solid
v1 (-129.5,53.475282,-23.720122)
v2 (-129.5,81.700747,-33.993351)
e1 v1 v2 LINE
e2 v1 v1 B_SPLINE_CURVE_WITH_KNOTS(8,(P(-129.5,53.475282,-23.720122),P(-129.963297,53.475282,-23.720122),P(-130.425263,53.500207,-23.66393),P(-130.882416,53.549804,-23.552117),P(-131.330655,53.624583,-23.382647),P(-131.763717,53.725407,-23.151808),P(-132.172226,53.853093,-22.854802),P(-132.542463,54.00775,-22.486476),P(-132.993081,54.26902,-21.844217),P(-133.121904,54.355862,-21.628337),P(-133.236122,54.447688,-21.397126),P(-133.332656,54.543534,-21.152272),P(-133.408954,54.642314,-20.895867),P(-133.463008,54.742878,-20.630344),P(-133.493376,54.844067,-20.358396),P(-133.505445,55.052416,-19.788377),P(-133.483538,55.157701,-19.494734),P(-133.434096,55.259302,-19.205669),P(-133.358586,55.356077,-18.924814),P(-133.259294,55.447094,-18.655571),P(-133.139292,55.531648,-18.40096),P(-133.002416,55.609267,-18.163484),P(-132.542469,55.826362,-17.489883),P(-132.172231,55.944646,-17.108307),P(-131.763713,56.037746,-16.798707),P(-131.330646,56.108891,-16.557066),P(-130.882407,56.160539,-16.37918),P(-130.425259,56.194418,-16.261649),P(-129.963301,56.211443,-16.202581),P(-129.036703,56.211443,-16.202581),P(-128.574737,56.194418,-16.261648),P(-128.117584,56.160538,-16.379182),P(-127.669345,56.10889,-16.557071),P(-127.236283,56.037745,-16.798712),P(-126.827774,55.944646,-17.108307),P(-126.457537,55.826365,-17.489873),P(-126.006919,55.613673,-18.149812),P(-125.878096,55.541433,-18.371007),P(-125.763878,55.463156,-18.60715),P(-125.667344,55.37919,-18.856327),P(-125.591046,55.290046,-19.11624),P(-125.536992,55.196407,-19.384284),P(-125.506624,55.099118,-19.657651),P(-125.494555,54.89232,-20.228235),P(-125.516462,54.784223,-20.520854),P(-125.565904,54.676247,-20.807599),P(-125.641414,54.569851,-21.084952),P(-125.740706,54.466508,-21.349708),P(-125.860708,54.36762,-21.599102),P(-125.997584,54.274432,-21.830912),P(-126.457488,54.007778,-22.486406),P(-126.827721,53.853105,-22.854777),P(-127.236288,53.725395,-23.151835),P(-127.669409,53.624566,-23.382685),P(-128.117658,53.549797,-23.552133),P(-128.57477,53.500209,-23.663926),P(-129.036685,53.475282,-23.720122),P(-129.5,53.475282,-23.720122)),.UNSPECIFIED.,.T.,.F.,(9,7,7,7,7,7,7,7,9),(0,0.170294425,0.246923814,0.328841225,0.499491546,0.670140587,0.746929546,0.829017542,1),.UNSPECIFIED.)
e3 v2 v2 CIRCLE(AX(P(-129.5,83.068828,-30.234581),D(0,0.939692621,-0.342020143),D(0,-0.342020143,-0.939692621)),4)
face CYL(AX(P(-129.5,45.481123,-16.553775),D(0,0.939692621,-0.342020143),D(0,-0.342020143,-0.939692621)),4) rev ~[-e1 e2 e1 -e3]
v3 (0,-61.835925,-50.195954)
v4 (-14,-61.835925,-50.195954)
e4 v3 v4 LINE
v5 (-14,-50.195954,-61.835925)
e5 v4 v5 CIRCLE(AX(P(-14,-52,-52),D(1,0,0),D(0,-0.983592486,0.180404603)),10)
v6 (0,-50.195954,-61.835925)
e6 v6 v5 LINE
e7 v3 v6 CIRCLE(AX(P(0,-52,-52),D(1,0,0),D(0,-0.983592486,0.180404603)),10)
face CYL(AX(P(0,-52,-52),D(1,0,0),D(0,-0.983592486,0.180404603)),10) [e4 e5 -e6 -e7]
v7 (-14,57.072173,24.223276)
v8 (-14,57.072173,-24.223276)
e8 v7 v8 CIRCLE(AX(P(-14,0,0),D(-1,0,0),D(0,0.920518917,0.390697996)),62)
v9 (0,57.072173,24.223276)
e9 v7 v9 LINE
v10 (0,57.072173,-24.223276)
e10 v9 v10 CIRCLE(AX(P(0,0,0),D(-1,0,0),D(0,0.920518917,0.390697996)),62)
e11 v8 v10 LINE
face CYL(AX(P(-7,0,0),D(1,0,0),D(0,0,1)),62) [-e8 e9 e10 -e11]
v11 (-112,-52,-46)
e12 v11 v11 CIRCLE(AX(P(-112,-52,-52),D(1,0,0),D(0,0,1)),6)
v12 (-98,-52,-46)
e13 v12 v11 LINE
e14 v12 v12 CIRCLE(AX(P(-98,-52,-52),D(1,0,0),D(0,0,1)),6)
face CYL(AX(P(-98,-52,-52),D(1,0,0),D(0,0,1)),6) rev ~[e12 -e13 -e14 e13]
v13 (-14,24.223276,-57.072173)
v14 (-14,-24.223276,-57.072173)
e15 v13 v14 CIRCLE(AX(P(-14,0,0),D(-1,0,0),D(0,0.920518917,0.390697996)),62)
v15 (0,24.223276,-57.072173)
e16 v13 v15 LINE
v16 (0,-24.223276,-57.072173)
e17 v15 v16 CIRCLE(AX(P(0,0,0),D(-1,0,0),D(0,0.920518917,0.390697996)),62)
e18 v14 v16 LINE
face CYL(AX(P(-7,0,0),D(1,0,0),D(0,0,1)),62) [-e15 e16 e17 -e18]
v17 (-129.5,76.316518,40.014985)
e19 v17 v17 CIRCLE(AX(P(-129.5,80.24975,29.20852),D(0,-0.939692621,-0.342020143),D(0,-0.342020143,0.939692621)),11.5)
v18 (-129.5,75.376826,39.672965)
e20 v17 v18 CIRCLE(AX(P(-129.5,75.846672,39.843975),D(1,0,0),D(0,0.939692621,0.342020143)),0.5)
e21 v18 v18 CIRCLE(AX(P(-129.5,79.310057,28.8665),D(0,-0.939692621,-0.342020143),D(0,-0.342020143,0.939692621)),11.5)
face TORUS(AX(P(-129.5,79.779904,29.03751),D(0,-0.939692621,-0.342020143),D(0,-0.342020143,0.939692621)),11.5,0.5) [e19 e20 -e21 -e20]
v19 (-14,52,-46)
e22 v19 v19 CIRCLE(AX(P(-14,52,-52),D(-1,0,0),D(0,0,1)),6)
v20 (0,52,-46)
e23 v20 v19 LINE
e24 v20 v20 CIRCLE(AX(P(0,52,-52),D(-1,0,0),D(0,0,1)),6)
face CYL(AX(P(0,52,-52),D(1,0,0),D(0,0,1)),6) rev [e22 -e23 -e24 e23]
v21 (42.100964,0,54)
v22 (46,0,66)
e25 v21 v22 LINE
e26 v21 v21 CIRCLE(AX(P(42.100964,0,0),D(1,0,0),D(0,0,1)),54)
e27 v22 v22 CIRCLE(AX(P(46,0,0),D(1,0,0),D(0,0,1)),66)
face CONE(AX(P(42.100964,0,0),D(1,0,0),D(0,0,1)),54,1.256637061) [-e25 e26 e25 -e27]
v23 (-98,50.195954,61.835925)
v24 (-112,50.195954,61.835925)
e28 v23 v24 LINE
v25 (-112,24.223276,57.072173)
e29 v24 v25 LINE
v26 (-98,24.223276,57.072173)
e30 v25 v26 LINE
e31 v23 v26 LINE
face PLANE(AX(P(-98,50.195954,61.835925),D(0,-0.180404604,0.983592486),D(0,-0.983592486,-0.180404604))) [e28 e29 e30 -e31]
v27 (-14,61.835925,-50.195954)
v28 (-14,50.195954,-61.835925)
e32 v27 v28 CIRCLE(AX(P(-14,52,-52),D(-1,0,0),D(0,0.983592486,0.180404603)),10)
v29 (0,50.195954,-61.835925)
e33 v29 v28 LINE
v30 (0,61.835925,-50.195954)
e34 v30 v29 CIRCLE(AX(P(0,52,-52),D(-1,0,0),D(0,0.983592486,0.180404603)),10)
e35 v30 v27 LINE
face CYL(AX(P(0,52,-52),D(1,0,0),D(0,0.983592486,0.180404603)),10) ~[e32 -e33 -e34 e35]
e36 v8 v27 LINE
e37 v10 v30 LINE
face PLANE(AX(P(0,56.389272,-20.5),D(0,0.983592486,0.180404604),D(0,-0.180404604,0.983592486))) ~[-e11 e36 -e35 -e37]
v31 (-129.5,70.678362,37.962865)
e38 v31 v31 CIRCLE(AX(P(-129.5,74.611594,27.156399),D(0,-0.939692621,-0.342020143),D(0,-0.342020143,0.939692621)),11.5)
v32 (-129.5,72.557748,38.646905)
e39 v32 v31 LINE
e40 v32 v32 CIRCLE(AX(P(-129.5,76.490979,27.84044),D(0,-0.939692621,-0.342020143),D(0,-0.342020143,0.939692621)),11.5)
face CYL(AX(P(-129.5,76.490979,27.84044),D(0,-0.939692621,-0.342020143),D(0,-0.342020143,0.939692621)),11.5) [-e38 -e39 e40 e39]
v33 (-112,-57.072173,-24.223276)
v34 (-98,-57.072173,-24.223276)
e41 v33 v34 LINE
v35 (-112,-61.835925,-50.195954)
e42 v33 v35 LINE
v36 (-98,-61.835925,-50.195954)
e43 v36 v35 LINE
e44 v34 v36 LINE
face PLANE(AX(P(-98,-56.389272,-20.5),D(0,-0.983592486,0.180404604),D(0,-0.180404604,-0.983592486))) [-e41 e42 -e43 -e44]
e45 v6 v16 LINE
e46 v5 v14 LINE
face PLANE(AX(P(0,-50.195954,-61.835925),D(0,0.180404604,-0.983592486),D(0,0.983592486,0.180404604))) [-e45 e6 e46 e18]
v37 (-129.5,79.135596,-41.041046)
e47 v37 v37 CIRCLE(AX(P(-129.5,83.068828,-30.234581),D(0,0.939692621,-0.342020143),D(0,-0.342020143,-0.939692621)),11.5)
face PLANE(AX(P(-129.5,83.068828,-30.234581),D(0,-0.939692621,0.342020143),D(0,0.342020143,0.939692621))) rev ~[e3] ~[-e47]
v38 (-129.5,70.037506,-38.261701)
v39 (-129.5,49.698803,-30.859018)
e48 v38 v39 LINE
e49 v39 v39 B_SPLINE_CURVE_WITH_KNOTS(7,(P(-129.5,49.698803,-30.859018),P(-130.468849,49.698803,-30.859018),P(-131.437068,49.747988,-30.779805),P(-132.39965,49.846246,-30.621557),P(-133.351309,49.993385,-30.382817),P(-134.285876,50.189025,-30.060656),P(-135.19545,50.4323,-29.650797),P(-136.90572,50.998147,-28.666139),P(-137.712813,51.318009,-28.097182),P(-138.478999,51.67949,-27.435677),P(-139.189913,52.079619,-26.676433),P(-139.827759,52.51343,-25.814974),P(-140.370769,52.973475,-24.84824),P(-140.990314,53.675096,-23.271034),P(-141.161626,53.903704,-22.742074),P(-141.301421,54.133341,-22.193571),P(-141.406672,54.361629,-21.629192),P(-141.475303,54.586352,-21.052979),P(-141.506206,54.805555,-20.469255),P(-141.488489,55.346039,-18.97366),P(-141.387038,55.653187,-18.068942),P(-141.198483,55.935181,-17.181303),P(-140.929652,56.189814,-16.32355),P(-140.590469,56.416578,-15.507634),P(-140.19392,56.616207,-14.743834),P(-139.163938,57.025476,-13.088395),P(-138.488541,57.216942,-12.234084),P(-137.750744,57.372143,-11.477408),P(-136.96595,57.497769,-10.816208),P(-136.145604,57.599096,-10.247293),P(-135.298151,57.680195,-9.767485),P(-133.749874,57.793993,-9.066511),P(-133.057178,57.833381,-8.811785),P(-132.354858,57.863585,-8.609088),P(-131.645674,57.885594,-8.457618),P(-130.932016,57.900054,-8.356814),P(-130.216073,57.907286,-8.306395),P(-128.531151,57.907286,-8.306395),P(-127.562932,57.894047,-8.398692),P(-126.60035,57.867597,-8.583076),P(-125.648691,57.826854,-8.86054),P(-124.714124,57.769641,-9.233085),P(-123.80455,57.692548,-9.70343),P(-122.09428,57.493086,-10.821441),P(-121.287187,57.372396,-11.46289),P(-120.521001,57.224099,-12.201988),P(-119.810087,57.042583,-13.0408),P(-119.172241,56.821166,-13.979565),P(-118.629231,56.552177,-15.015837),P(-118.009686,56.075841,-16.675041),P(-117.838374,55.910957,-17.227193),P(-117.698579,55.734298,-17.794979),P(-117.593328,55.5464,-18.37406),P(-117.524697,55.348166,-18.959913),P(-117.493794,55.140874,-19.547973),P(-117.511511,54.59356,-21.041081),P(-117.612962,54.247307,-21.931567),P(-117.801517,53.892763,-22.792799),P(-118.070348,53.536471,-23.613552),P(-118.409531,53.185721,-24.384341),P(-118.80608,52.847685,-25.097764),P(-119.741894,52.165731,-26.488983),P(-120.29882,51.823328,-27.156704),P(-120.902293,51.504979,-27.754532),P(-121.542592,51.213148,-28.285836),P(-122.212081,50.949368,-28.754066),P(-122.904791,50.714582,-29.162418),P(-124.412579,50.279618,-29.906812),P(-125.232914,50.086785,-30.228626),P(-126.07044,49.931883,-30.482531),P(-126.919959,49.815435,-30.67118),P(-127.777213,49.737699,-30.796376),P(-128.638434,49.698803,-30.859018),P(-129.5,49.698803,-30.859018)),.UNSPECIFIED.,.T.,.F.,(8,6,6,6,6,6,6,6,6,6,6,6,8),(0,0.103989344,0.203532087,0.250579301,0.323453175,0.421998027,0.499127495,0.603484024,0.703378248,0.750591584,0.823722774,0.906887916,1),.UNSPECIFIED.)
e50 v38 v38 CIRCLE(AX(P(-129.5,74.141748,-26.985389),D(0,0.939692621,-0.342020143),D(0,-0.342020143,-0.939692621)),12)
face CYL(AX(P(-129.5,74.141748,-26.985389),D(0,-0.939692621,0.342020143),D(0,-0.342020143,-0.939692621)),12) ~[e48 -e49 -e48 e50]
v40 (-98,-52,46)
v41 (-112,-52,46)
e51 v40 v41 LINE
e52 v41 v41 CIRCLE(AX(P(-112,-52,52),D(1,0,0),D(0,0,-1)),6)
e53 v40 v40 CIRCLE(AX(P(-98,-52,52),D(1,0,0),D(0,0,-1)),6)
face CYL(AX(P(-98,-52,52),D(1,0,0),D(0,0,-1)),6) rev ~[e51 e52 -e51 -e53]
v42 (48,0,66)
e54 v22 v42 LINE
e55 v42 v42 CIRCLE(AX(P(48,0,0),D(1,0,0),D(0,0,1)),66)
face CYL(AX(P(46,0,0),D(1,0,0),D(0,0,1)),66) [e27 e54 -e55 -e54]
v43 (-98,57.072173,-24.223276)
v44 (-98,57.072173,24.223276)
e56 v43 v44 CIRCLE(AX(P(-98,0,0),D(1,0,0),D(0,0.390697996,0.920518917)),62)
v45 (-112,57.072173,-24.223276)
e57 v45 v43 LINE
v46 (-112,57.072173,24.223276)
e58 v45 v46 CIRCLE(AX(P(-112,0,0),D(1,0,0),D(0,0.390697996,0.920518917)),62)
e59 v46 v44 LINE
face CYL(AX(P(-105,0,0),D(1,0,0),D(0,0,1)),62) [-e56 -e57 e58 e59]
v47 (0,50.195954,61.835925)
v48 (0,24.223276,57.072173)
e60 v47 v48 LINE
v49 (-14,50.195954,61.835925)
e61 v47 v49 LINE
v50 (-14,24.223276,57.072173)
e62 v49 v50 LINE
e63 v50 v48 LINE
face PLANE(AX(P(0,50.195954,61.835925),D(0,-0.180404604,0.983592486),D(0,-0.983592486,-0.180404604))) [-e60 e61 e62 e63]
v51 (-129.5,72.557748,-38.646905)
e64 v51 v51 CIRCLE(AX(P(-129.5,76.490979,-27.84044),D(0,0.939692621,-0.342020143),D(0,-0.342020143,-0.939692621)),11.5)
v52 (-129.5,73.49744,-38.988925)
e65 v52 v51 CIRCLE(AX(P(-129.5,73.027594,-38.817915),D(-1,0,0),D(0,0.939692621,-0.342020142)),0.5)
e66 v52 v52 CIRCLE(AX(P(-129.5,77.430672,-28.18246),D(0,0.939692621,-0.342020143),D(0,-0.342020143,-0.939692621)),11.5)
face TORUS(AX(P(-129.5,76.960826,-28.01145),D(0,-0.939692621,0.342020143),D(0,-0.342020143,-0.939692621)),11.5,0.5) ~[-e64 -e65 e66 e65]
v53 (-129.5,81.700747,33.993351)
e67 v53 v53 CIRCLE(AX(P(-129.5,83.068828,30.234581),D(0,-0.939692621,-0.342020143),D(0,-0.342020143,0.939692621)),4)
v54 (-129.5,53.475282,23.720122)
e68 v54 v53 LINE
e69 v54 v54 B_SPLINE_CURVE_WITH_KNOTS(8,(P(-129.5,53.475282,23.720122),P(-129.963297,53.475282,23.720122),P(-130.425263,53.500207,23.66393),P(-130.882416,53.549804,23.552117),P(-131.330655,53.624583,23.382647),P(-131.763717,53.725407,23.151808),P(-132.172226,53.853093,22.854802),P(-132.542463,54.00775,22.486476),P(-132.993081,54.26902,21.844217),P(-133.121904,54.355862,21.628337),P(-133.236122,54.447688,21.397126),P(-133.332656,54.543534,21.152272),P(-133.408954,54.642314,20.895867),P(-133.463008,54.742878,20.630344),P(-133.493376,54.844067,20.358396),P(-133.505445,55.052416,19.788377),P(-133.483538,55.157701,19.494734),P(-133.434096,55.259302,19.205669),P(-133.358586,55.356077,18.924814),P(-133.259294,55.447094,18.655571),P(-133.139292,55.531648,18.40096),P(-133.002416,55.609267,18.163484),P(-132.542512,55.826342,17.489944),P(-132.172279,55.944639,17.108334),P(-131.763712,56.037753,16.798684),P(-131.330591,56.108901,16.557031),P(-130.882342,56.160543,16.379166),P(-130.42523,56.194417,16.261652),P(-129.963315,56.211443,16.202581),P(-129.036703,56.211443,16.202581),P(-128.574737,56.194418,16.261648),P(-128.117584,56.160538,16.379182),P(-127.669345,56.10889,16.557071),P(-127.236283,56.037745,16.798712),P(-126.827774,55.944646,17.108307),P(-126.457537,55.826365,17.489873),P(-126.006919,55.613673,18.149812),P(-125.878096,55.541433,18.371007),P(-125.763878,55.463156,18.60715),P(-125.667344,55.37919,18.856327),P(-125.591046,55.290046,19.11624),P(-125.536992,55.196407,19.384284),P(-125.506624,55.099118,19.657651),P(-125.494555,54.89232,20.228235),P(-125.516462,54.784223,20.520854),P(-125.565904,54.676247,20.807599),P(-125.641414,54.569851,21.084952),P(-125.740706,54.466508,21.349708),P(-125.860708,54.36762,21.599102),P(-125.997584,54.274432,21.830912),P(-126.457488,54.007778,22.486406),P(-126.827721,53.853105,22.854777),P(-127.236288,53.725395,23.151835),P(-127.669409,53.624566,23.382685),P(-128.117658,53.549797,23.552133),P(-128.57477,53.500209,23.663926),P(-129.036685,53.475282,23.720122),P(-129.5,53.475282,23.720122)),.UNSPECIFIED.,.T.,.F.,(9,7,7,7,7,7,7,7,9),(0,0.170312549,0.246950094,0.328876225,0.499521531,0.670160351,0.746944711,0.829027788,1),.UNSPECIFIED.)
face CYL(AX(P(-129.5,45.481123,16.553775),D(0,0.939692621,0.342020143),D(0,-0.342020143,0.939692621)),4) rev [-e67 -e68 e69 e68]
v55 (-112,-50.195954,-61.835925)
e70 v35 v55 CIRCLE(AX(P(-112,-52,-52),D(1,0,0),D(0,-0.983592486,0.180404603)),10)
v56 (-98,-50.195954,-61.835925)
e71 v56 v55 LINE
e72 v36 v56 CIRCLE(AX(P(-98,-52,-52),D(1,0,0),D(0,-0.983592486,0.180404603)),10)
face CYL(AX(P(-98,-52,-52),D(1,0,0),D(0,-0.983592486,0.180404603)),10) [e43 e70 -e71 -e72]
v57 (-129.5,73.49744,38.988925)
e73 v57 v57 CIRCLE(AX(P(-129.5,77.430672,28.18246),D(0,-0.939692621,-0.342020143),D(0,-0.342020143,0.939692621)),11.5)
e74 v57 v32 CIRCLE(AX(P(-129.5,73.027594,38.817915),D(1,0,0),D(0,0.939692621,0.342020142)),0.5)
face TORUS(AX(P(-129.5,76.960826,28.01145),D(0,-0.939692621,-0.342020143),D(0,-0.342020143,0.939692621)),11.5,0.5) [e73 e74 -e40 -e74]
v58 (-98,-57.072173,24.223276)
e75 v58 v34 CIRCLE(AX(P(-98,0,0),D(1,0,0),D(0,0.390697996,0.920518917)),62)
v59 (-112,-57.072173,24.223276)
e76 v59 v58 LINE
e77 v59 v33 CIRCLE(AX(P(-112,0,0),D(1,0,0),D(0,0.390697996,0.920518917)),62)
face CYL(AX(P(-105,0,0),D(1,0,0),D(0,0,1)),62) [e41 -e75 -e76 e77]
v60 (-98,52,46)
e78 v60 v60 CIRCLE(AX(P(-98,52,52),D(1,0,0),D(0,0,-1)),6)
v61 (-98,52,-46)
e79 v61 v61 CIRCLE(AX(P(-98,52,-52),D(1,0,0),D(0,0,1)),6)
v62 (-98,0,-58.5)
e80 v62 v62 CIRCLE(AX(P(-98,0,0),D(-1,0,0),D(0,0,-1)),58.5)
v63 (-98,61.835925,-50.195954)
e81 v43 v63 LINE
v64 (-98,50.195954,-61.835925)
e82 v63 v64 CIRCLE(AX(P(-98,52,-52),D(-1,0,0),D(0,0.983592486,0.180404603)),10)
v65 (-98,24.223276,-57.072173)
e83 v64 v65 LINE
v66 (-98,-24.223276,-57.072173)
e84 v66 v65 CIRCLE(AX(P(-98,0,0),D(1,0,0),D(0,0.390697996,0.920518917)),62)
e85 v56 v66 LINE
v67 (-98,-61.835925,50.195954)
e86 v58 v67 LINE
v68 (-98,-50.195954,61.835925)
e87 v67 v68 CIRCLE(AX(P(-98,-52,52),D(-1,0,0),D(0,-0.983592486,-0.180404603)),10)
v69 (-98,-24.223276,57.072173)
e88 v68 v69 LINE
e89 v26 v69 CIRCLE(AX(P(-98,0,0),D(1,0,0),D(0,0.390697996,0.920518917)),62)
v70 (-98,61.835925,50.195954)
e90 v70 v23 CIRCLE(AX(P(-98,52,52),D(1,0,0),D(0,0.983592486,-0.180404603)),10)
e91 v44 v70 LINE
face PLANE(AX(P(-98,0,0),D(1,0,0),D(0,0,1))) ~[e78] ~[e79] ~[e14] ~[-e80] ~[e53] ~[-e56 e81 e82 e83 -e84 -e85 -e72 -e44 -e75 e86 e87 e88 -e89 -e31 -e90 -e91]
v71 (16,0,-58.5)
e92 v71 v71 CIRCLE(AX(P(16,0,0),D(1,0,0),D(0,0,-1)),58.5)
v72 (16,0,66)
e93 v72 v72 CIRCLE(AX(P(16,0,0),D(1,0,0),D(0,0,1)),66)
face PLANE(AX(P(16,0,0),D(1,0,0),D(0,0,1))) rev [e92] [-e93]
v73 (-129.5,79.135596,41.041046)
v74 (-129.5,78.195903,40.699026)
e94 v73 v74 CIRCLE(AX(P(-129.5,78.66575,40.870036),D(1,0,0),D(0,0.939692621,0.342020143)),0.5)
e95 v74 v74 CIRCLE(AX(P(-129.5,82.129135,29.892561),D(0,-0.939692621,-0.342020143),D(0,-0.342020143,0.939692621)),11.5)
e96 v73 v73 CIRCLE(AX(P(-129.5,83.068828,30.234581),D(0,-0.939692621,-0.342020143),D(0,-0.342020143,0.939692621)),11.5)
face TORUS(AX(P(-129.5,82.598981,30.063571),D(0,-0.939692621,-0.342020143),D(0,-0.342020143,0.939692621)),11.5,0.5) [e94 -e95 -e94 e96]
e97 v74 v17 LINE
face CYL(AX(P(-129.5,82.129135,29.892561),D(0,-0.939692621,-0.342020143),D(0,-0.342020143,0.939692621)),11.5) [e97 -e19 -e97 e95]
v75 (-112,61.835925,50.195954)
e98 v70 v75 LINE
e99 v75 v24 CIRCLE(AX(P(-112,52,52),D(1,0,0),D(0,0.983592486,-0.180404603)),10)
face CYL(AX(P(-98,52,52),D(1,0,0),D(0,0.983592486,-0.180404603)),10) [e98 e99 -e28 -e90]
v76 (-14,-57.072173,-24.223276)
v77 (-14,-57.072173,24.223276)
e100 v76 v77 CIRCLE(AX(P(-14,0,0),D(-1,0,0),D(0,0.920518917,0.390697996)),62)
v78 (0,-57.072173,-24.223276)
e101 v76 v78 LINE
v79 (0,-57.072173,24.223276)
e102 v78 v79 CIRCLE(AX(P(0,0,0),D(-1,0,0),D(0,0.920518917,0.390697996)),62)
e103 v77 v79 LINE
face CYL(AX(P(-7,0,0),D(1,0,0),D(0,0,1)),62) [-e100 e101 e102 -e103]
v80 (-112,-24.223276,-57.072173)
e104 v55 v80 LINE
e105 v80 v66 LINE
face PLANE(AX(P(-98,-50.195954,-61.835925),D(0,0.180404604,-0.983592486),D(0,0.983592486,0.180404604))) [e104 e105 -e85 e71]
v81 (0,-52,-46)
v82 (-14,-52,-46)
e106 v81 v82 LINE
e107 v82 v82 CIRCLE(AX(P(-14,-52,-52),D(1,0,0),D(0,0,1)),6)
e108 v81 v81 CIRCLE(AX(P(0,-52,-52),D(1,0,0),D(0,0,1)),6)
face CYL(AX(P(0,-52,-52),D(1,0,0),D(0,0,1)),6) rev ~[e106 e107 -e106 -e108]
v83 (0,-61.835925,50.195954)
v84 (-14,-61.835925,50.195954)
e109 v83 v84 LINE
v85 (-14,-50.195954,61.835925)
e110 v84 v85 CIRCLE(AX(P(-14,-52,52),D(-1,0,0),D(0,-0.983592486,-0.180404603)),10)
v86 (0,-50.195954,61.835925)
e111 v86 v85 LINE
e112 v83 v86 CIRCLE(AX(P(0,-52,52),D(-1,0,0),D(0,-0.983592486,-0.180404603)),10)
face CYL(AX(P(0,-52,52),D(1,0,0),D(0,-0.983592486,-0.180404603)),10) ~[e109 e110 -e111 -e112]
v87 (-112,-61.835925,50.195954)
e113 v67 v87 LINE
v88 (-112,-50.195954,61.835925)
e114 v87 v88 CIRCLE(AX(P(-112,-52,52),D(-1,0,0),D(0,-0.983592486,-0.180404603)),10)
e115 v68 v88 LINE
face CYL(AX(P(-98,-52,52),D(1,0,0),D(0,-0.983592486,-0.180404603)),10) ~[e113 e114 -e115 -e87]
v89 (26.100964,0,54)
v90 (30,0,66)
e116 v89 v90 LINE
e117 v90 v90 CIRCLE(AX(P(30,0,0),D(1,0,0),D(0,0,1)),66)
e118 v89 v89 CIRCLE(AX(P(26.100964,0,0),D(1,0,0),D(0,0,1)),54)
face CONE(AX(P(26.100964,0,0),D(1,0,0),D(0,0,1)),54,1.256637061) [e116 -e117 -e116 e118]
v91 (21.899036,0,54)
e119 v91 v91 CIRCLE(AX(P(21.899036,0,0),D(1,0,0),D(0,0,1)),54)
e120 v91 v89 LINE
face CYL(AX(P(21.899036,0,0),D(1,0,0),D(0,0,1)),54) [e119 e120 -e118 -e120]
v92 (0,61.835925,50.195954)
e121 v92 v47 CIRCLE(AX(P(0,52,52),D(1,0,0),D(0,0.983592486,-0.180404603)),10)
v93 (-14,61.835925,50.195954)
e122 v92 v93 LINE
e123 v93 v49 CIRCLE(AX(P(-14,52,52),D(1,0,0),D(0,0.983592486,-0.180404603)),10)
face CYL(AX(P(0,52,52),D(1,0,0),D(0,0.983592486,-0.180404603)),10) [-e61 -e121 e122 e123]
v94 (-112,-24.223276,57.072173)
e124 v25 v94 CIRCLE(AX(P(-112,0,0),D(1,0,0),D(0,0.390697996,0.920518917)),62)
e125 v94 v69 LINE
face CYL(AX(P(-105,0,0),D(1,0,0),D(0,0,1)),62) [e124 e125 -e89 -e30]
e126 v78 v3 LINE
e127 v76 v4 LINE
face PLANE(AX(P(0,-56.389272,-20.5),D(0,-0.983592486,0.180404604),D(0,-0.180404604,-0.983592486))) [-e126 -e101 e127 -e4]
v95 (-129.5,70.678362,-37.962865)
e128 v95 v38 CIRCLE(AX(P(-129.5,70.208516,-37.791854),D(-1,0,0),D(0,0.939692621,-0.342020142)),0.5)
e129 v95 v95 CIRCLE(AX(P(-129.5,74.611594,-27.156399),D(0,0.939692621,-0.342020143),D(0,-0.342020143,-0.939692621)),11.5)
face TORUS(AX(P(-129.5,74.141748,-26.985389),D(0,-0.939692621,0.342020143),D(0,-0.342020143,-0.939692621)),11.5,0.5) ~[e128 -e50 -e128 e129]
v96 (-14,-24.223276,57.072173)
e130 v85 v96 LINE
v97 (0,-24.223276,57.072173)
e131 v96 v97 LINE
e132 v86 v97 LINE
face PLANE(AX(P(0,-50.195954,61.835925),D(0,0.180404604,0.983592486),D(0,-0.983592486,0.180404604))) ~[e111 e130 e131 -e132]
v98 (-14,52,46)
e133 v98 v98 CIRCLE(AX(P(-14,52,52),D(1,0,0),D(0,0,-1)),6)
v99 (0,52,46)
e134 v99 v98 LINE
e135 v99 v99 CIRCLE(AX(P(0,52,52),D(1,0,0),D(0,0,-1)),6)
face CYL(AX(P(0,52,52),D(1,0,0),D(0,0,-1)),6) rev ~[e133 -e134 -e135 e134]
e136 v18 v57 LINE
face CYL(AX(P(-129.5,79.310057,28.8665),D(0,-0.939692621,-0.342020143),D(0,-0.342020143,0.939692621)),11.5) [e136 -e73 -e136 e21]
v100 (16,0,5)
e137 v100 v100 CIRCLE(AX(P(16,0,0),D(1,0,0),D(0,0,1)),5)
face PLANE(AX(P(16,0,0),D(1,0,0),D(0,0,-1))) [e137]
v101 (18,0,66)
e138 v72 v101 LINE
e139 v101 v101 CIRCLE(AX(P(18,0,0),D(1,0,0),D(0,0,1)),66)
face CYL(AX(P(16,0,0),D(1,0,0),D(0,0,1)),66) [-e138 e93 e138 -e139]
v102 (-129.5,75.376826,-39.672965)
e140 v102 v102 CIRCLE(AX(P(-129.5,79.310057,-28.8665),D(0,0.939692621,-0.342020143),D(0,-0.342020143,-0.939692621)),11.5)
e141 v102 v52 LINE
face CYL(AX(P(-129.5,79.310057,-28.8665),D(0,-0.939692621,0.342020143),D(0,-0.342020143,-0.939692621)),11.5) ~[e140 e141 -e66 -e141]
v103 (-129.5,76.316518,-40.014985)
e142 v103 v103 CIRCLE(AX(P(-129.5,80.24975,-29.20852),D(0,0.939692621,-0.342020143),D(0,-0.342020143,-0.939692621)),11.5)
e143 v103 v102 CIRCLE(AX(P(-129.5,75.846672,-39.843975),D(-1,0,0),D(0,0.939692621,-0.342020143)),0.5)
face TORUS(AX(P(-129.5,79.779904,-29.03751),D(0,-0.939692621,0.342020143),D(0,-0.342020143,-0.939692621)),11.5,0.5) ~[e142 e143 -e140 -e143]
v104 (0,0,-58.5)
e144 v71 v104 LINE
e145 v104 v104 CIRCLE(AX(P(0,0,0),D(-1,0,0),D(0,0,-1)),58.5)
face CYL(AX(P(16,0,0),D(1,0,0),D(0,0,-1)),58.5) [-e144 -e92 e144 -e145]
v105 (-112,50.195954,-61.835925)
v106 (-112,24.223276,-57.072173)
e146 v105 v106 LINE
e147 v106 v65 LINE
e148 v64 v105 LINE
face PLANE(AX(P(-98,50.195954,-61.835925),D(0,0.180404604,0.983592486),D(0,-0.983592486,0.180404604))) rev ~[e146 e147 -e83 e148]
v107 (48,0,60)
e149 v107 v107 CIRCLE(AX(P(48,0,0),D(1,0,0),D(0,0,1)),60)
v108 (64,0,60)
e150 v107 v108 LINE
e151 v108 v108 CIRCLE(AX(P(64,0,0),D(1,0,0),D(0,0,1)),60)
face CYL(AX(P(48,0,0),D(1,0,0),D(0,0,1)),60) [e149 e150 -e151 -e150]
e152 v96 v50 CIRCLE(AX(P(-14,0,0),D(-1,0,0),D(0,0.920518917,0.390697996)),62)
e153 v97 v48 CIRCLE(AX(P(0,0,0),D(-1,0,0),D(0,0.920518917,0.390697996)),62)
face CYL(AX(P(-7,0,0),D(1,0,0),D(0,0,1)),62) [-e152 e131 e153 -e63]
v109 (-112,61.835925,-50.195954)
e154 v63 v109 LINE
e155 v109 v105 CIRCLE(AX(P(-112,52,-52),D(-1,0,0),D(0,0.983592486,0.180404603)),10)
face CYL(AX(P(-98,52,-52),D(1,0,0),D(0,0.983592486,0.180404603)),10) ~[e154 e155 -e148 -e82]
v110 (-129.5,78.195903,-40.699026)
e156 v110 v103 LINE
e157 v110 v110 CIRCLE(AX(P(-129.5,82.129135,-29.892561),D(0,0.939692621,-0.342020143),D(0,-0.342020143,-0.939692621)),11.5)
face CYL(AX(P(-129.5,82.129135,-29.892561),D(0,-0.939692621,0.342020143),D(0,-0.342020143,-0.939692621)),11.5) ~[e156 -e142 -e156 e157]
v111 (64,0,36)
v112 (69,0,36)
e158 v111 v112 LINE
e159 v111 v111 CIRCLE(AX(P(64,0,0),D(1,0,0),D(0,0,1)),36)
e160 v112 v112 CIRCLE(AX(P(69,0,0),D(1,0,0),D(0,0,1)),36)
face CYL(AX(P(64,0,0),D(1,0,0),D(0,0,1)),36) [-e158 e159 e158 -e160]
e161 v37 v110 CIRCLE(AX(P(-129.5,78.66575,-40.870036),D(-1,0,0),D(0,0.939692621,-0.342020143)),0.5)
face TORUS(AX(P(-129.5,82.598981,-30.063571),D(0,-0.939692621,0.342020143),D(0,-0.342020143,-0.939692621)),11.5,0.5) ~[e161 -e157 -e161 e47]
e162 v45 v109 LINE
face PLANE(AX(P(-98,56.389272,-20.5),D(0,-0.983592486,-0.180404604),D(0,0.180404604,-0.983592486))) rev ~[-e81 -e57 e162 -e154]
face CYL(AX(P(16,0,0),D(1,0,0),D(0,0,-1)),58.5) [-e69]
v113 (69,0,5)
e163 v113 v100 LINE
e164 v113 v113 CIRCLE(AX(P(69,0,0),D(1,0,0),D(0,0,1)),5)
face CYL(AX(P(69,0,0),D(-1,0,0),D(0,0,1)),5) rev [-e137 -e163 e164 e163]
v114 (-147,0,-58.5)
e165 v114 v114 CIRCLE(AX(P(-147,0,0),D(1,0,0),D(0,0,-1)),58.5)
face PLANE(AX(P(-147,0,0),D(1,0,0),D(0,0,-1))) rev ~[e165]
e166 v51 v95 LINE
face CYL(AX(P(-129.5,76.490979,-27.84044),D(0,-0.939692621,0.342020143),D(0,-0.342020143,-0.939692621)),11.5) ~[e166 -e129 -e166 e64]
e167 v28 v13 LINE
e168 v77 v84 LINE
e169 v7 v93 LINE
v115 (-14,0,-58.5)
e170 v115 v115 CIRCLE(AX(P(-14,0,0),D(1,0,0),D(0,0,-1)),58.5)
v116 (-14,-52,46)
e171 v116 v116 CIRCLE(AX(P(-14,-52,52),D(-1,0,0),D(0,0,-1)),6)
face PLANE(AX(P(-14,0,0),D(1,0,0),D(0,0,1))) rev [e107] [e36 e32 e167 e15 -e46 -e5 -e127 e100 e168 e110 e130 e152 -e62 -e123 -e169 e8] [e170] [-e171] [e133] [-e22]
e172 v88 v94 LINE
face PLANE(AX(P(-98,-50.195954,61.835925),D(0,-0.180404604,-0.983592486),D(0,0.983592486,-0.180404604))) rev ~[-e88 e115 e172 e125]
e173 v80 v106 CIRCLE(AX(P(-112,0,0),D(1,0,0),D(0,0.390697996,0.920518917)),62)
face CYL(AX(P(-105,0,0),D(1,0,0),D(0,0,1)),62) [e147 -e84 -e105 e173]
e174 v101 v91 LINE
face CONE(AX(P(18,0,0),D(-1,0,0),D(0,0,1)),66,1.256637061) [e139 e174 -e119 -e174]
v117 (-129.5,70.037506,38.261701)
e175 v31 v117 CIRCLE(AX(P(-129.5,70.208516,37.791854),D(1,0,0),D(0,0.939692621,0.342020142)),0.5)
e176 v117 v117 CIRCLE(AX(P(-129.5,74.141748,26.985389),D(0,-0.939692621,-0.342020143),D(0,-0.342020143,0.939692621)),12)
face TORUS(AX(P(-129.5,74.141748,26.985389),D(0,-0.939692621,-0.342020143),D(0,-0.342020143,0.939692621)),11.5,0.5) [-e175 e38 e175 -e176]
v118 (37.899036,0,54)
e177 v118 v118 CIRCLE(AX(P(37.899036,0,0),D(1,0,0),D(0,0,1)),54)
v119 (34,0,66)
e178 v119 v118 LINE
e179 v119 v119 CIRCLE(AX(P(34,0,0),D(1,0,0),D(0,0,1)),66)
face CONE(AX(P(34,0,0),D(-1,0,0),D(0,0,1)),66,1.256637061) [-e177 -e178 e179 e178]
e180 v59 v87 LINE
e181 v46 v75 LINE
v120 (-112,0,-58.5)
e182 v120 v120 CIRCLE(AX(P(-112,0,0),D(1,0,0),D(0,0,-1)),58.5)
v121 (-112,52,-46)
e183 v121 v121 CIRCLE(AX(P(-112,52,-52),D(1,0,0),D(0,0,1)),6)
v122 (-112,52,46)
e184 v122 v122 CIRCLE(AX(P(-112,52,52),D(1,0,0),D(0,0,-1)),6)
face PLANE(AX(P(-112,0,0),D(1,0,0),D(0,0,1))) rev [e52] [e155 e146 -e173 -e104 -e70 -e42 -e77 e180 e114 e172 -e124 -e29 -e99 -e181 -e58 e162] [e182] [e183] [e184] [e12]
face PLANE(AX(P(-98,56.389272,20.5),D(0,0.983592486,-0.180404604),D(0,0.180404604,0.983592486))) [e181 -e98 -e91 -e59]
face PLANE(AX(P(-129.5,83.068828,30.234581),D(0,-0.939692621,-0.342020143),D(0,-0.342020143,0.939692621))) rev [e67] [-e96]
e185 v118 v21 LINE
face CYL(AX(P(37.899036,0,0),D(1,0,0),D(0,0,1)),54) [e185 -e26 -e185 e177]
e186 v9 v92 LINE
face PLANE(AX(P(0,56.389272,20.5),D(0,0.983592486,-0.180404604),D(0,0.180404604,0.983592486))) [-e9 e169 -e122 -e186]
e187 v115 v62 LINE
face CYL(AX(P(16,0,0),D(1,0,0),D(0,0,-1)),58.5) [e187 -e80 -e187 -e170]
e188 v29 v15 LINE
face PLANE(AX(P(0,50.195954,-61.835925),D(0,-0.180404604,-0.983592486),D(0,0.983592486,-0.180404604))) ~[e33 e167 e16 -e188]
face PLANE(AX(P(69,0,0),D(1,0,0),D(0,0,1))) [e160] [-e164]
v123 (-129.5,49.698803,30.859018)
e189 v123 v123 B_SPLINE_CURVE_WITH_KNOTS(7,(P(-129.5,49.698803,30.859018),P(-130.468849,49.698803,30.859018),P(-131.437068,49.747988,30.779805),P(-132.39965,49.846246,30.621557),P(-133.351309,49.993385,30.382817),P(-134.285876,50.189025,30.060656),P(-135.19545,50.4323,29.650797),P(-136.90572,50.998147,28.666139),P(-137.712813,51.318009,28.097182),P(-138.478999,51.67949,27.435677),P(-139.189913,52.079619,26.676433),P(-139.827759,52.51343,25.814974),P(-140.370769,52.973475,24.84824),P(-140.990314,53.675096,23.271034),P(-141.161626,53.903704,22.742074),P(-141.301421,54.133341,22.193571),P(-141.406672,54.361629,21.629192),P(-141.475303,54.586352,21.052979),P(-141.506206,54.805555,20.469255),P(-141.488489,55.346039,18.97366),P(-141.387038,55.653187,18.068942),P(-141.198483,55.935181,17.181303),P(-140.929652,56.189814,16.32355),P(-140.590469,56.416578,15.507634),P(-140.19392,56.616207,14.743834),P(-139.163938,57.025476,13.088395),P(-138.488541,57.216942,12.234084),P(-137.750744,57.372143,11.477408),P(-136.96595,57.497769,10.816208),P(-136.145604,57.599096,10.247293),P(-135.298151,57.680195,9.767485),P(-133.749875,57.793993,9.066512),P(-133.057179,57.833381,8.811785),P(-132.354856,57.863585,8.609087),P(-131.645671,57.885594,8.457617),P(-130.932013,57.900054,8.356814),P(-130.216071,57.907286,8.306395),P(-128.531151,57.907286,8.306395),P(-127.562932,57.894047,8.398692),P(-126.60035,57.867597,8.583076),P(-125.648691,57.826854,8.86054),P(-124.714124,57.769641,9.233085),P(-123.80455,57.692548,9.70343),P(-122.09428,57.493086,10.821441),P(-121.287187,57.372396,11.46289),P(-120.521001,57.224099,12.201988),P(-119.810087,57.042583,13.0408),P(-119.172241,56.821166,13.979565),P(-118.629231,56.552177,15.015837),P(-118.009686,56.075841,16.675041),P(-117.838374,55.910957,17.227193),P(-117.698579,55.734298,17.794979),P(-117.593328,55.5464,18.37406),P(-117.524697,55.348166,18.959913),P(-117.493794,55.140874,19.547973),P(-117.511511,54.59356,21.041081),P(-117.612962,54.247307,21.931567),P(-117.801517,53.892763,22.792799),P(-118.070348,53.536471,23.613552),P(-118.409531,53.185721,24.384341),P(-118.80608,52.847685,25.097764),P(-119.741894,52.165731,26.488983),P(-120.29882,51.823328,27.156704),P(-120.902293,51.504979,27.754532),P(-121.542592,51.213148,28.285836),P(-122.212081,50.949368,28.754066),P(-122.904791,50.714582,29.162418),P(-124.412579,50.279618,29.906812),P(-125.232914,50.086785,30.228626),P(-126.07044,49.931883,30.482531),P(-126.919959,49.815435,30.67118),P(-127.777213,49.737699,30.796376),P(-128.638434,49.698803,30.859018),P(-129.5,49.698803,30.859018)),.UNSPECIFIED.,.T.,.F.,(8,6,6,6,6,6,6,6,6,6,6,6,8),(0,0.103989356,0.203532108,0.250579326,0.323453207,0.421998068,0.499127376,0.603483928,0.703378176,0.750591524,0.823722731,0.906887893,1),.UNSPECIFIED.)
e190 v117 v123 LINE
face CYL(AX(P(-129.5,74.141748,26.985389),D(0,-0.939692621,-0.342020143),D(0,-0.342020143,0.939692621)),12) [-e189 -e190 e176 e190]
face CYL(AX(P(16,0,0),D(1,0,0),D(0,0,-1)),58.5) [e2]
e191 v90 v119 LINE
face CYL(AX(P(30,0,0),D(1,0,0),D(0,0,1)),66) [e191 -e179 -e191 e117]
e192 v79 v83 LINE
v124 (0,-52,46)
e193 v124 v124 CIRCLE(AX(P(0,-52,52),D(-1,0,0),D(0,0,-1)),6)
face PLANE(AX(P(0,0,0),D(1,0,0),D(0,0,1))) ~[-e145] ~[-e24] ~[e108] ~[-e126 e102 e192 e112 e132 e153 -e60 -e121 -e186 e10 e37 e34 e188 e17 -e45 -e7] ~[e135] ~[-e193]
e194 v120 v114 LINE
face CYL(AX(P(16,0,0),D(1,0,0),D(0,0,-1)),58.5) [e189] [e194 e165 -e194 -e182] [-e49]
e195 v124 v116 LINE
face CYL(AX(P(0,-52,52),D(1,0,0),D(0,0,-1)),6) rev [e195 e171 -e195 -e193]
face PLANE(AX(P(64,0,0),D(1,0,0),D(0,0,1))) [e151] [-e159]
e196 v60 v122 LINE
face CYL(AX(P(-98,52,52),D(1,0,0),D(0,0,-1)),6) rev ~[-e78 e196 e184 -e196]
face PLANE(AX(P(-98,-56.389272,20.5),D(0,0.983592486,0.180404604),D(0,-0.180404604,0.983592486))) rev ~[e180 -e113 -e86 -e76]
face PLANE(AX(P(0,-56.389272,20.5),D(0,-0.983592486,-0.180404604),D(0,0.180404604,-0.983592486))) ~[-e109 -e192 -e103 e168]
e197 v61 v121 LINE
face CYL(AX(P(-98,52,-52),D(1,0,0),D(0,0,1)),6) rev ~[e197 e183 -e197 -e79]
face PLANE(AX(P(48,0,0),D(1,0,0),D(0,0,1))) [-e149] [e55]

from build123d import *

# Parameters (mm, degrees)
SKETCH1_R                 = 58.5
BOSS_EXTRUDE1_DEPTH       = 147
BOSS_EXTRUDE2_START       = 16
SKETCH2_R                 = 58.5
BOSS_EXTRUDE2_DEPTH       = 16
SKETCH3_W                 = 14
SKETCH3_H                 = 3.5
SKETCH6_R                 = 6
BOSS_EXTRUDE3_DEPTH       = 14
MIRROR3_COPY_1_SKETCH_R   = 6
MIRROR3_COPY_1_DEPTH      = 14
LPATTERN1_COUNT           = 2
LPATTERN1_PITCH           = 98
LPATTERN1_COPY_1_SKETCH_R = 6
LPATTERN1_COPY_1_DEPTH    = 14
LPATTERN1_COPY_2_SKETCH_R = 6
LPATTERN1_COPY_2_DEPTH    = 14
LPATTERN1_COPY_3_SKETCH_R = 6
LPATTERN1_COPY_3_DEPTH    = 14


with BuildPart() as part:
    # Sketch1 → Boss-Extrude1 (new body)
    with BuildSketch(Plane(origin=(0, 0, 0), x_dir=(0, 0, -1), z_dir=(1, 0, 0))):
        Circle(SKETCH1_R)
    extrude(amount=-BOSS_EXTRUDE1_DEPTH)

    # Sketch2 → Boss-Extrude2 (add)
    with BuildSketch(Plane(origin=(0, 0, 0), x_dir=(0, 0, -1), z_dir=(1, 0, 0)).offset(BOSS_EXTRUDE2_START)):
        Circle(SKETCH2_R)
    extrude(amount=-BOSS_EXTRUDE2_DEPTH)

    # Sketch3 → Revolve1 (revolve)
    with BuildSketch(Plane.XY, mode=Mode.PRIVATE) as revolve1_sk:
        Polygon((16, 5), (16, 66), (18, 66), (21.899036355, 54), (26.100963645, 54), (30, 66), (34, 66), (37.899036355, 54), (42.100963645, 54), (46, 66), (48, 66), (48, 60), (64, 60), (64, 36), (69, 36), (69, 5), align=None)
        with Locations((-7, 60.25)):
            Rectangle(SKETCH3_W, SKETCH3_H)
        with Locations((-105, 60.25)):
            Rectangle(SKETCH3_W, SKETCH3_H)
    revolve(revolve1_sk.sketch.rotate(Axis((-162.78049782, 0, 0), (1, 0, 0)), 90), axis=Axis((-162.78049782, 0, 0), (1, 0, 0)))

    # Sketch5 → Revolve2 (revolve)
    with BuildSketch(Plane(origin=(-129.5, 0, 0), x_dir=(0, 0, -1), z_dir=(1, 0, 0))):
        with BuildLine():
            Line((-33.993351153, 81.700747104), (-41.041045809, 79.135596029))
            ThreePointArc((-41.041045809, 79.135596029), (-41.339882048, 78.494739647), (-40.699025666, 78.195903408))
            Line((-40.699025666, 78.195903408), (-40.014985379, 76.316518167))
            ThreePointArc((-40.014985379, 76.316518167), (-40.313821618, 75.675661785), (-39.672965236, 75.376825546))
            Line((-39.672965236, 75.376825546), (-38.988924949, 73.497440305))
            ThreePointArc((-38.988924949, 73.497440305), (-39.287761188, 72.856583922), (-38.646904806, 72.557747684))
            Line((-38.646904806, 72.557747684), (-37.962864519, 70.678362442))
            ThreePointArc((-37.962864519, 70.678362442), (-38.245008341, 70.419825263), (-38.261700758, 70.03750606))
            Line((-38.261700758, 70.03750606), (-27.830086386, 41.376881126))
            Line((-27.830086386, 41.376881126), (-20.31254542, 44.113042273))
            Line((-20.31254542, 44.113042273), (-33.993351153, 81.700747104))
        make_face()
    revolve2 = revolve(axis=Axis((-129.5, 87.36363996, 31.797764503), (0, -0.9396926207859081, -0.34202014332566955)))

    # Mirror1: Revolve2 across plane
    add(revolve2.mirror(Plane.XY))

    # Sketch6 → Boss-Extrude3 (add)
    with BuildSketch(Plane(origin=(0, 0, 0), x_dir=(0, 0, -1), z_dir=(1, 0, 0))):
        with BuildLine():
            Line((-56.389272029, 20.5), (-49.764441168, 13.875169139))
            Line((-49.764441168, 13.875169139), (-13.875169139, 49.764441168))
            Line((-13.875169139, 49.764441168), (-20.5, 56.389272029))
            Line((-20.5, 56.389272029), (-50.195953965, 61.835924863))
            ThreePointArc((-50.195953965, 61.835924863), (-59.071067812, 59.071067812), (-61.835924863, 50.195953965))
            Line((-61.835924863, 50.195953965), (-56.389272029, 20.5))
        make_face()
        with Locations((-52, 52)):
            Circle(SKETCH6_R, mode=Mode.SUBTRACT)
    boss_extrude3 = extrude(amount=-BOSS_EXTRUDE3_DEPTH)

    # Mirror2: Boss-Extrude3 across plane
    add(boss_extrude3.mirror(Plane.XY))

    # Mirror3: Boss-Extrude3 across plane
    add(boss_extrude3.mirror(Plane.ZX))

    # Mirror3 copy 1 sketch → Mirror3 copy 1 (add)
    with BuildSketch(Plane(origin=(0, 0, 0), x_dir=(0, 0, 1), z_dir=(1, 0, 0))):
        with BuildLine():
            Line((-56.389272029, 20.5), (-49.764441168, 13.875169139))
            Line((-49.764441168, 13.875169139), (-13.875169139, 49.764441168))
            Line((-13.875169139, 49.764441168), (-20.5, 56.389272029))
            Line((-20.5, 56.389272029), (-50.195953965, 61.835924863))
            ThreePointArc((-50.195953965, 61.835924863), (-59.071067812, 59.071067812), (-61.835924863, 50.195953965))
            Line((-61.835924863, 50.195953965), (-56.389272029, 20.5))
        make_face()
        with Locations((-52, 52)):
            Circle(MIRROR3_COPY_1_SKETCH_R, mode=Mode.SUBTRACT)
    extrude(amount=-MIRROR3_COPY_1_DEPTH)

    # LPattern1: Boss-Extrude3 ×2
    with Locations(*[(-i * LPATTERN1_PITCH, 0, 0) for i in range(1, LPATTERN1_COUNT)]):
        add(boss_extrude3)

    # LPattern1 copy 1 sketch → LPattern1 copy 1 (add)
    with BuildSketch(Plane(origin=(-98, 0, 0), x_dir=(0, 0, 1), z_dir=(1, 0, 0))):
        with BuildLine():
            Line((-56.389272029, -20.5), (-49.764441168, -13.875169139))
            Line((-49.764441168, -13.875169139), (-13.875169139, -49.764441168))
            Line((-13.875169139, -49.764441168), (-20.5, -56.389272029))
            Line((-20.5, -56.389272029), (-50.195953965, -61.835924863))
            ThreePointArc((-50.195953965, -61.835924863), (-59.071067812, -59.071067812), (-61.835924863, -50.195953965))
            Line((-61.835924863, -50.195953965), (-56.389272029, -20.5))
        make_face()
        with Locations((-52, -52)):
            Circle(LPATTERN1_COPY_1_SKETCH_R, mode=Mode.SUBTRACT)
    extrude(amount=-LPATTERN1_COPY_1_DEPTH)

    # LPattern1 copy 2 sketch → LPattern1 copy 2 (add)
    with BuildSketch(Plane(origin=(-98, 0, 0), x_dir=(0, 0, -1), z_dir=(1, 0, 0))):
        with BuildLine():
            Line((-56.389272029, -20.5), (-49.764441168, -13.875169139))
            Line((-49.764441168, -13.875169139), (-13.875169139, -49.764441168))
            Line((-13.875169139, -49.764441168), (-20.5, -56.389272029))
            Line((-20.5, -56.389272029), (-50.195953965, -61.835924863))
            ThreePointArc((-50.195953965, -61.835924863), (-59.071067812, -59.071067812), (-61.835924863, -50.195953965))
            Line((-61.835924863, -50.195953965), (-56.389272029, -20.5))
        make_face()
        with Locations((-52, -52)):
            Circle(LPATTERN1_COPY_2_SKETCH_R, mode=Mode.SUBTRACT)
    extrude(amount=-LPATTERN1_COPY_2_DEPTH)

    # LPattern1 copy 3 sketch → LPattern1 copy 3 (add)
    with BuildSketch(Plane(origin=(-98, 0, 0), x_dir=(0, 0, 1), z_dir=(1, 0, 0))):
        with BuildLine():
            Line((-56.389272029, 20.5), (-49.764441168, 13.875169139))
            Line((-49.764441168, 13.875169139), (-13.875169139, 49.764441168))
            Line((-13.875169139, 49.764441168), (-20.5, 56.389272029))
            Line((-20.5, 56.389272029), (-50.195953965, 61.835924863))
            ThreePointArc((-50.195953965, 61.835924863), (-59.071067812, 59.071067812), (-61.835924863, 50.195953965))
            Line((-61.835924863, 50.195953965), (-56.389272029, 20.5))
        make_face()
        with Locations((-52, 52)):
            Circle(LPATTERN1_COPY_3_SKETCH_R, mode=Mode.SUBTRACT)
    extrude(amount=-LPATTERN1_COPY_3_DEPTH)


solid = part.part
